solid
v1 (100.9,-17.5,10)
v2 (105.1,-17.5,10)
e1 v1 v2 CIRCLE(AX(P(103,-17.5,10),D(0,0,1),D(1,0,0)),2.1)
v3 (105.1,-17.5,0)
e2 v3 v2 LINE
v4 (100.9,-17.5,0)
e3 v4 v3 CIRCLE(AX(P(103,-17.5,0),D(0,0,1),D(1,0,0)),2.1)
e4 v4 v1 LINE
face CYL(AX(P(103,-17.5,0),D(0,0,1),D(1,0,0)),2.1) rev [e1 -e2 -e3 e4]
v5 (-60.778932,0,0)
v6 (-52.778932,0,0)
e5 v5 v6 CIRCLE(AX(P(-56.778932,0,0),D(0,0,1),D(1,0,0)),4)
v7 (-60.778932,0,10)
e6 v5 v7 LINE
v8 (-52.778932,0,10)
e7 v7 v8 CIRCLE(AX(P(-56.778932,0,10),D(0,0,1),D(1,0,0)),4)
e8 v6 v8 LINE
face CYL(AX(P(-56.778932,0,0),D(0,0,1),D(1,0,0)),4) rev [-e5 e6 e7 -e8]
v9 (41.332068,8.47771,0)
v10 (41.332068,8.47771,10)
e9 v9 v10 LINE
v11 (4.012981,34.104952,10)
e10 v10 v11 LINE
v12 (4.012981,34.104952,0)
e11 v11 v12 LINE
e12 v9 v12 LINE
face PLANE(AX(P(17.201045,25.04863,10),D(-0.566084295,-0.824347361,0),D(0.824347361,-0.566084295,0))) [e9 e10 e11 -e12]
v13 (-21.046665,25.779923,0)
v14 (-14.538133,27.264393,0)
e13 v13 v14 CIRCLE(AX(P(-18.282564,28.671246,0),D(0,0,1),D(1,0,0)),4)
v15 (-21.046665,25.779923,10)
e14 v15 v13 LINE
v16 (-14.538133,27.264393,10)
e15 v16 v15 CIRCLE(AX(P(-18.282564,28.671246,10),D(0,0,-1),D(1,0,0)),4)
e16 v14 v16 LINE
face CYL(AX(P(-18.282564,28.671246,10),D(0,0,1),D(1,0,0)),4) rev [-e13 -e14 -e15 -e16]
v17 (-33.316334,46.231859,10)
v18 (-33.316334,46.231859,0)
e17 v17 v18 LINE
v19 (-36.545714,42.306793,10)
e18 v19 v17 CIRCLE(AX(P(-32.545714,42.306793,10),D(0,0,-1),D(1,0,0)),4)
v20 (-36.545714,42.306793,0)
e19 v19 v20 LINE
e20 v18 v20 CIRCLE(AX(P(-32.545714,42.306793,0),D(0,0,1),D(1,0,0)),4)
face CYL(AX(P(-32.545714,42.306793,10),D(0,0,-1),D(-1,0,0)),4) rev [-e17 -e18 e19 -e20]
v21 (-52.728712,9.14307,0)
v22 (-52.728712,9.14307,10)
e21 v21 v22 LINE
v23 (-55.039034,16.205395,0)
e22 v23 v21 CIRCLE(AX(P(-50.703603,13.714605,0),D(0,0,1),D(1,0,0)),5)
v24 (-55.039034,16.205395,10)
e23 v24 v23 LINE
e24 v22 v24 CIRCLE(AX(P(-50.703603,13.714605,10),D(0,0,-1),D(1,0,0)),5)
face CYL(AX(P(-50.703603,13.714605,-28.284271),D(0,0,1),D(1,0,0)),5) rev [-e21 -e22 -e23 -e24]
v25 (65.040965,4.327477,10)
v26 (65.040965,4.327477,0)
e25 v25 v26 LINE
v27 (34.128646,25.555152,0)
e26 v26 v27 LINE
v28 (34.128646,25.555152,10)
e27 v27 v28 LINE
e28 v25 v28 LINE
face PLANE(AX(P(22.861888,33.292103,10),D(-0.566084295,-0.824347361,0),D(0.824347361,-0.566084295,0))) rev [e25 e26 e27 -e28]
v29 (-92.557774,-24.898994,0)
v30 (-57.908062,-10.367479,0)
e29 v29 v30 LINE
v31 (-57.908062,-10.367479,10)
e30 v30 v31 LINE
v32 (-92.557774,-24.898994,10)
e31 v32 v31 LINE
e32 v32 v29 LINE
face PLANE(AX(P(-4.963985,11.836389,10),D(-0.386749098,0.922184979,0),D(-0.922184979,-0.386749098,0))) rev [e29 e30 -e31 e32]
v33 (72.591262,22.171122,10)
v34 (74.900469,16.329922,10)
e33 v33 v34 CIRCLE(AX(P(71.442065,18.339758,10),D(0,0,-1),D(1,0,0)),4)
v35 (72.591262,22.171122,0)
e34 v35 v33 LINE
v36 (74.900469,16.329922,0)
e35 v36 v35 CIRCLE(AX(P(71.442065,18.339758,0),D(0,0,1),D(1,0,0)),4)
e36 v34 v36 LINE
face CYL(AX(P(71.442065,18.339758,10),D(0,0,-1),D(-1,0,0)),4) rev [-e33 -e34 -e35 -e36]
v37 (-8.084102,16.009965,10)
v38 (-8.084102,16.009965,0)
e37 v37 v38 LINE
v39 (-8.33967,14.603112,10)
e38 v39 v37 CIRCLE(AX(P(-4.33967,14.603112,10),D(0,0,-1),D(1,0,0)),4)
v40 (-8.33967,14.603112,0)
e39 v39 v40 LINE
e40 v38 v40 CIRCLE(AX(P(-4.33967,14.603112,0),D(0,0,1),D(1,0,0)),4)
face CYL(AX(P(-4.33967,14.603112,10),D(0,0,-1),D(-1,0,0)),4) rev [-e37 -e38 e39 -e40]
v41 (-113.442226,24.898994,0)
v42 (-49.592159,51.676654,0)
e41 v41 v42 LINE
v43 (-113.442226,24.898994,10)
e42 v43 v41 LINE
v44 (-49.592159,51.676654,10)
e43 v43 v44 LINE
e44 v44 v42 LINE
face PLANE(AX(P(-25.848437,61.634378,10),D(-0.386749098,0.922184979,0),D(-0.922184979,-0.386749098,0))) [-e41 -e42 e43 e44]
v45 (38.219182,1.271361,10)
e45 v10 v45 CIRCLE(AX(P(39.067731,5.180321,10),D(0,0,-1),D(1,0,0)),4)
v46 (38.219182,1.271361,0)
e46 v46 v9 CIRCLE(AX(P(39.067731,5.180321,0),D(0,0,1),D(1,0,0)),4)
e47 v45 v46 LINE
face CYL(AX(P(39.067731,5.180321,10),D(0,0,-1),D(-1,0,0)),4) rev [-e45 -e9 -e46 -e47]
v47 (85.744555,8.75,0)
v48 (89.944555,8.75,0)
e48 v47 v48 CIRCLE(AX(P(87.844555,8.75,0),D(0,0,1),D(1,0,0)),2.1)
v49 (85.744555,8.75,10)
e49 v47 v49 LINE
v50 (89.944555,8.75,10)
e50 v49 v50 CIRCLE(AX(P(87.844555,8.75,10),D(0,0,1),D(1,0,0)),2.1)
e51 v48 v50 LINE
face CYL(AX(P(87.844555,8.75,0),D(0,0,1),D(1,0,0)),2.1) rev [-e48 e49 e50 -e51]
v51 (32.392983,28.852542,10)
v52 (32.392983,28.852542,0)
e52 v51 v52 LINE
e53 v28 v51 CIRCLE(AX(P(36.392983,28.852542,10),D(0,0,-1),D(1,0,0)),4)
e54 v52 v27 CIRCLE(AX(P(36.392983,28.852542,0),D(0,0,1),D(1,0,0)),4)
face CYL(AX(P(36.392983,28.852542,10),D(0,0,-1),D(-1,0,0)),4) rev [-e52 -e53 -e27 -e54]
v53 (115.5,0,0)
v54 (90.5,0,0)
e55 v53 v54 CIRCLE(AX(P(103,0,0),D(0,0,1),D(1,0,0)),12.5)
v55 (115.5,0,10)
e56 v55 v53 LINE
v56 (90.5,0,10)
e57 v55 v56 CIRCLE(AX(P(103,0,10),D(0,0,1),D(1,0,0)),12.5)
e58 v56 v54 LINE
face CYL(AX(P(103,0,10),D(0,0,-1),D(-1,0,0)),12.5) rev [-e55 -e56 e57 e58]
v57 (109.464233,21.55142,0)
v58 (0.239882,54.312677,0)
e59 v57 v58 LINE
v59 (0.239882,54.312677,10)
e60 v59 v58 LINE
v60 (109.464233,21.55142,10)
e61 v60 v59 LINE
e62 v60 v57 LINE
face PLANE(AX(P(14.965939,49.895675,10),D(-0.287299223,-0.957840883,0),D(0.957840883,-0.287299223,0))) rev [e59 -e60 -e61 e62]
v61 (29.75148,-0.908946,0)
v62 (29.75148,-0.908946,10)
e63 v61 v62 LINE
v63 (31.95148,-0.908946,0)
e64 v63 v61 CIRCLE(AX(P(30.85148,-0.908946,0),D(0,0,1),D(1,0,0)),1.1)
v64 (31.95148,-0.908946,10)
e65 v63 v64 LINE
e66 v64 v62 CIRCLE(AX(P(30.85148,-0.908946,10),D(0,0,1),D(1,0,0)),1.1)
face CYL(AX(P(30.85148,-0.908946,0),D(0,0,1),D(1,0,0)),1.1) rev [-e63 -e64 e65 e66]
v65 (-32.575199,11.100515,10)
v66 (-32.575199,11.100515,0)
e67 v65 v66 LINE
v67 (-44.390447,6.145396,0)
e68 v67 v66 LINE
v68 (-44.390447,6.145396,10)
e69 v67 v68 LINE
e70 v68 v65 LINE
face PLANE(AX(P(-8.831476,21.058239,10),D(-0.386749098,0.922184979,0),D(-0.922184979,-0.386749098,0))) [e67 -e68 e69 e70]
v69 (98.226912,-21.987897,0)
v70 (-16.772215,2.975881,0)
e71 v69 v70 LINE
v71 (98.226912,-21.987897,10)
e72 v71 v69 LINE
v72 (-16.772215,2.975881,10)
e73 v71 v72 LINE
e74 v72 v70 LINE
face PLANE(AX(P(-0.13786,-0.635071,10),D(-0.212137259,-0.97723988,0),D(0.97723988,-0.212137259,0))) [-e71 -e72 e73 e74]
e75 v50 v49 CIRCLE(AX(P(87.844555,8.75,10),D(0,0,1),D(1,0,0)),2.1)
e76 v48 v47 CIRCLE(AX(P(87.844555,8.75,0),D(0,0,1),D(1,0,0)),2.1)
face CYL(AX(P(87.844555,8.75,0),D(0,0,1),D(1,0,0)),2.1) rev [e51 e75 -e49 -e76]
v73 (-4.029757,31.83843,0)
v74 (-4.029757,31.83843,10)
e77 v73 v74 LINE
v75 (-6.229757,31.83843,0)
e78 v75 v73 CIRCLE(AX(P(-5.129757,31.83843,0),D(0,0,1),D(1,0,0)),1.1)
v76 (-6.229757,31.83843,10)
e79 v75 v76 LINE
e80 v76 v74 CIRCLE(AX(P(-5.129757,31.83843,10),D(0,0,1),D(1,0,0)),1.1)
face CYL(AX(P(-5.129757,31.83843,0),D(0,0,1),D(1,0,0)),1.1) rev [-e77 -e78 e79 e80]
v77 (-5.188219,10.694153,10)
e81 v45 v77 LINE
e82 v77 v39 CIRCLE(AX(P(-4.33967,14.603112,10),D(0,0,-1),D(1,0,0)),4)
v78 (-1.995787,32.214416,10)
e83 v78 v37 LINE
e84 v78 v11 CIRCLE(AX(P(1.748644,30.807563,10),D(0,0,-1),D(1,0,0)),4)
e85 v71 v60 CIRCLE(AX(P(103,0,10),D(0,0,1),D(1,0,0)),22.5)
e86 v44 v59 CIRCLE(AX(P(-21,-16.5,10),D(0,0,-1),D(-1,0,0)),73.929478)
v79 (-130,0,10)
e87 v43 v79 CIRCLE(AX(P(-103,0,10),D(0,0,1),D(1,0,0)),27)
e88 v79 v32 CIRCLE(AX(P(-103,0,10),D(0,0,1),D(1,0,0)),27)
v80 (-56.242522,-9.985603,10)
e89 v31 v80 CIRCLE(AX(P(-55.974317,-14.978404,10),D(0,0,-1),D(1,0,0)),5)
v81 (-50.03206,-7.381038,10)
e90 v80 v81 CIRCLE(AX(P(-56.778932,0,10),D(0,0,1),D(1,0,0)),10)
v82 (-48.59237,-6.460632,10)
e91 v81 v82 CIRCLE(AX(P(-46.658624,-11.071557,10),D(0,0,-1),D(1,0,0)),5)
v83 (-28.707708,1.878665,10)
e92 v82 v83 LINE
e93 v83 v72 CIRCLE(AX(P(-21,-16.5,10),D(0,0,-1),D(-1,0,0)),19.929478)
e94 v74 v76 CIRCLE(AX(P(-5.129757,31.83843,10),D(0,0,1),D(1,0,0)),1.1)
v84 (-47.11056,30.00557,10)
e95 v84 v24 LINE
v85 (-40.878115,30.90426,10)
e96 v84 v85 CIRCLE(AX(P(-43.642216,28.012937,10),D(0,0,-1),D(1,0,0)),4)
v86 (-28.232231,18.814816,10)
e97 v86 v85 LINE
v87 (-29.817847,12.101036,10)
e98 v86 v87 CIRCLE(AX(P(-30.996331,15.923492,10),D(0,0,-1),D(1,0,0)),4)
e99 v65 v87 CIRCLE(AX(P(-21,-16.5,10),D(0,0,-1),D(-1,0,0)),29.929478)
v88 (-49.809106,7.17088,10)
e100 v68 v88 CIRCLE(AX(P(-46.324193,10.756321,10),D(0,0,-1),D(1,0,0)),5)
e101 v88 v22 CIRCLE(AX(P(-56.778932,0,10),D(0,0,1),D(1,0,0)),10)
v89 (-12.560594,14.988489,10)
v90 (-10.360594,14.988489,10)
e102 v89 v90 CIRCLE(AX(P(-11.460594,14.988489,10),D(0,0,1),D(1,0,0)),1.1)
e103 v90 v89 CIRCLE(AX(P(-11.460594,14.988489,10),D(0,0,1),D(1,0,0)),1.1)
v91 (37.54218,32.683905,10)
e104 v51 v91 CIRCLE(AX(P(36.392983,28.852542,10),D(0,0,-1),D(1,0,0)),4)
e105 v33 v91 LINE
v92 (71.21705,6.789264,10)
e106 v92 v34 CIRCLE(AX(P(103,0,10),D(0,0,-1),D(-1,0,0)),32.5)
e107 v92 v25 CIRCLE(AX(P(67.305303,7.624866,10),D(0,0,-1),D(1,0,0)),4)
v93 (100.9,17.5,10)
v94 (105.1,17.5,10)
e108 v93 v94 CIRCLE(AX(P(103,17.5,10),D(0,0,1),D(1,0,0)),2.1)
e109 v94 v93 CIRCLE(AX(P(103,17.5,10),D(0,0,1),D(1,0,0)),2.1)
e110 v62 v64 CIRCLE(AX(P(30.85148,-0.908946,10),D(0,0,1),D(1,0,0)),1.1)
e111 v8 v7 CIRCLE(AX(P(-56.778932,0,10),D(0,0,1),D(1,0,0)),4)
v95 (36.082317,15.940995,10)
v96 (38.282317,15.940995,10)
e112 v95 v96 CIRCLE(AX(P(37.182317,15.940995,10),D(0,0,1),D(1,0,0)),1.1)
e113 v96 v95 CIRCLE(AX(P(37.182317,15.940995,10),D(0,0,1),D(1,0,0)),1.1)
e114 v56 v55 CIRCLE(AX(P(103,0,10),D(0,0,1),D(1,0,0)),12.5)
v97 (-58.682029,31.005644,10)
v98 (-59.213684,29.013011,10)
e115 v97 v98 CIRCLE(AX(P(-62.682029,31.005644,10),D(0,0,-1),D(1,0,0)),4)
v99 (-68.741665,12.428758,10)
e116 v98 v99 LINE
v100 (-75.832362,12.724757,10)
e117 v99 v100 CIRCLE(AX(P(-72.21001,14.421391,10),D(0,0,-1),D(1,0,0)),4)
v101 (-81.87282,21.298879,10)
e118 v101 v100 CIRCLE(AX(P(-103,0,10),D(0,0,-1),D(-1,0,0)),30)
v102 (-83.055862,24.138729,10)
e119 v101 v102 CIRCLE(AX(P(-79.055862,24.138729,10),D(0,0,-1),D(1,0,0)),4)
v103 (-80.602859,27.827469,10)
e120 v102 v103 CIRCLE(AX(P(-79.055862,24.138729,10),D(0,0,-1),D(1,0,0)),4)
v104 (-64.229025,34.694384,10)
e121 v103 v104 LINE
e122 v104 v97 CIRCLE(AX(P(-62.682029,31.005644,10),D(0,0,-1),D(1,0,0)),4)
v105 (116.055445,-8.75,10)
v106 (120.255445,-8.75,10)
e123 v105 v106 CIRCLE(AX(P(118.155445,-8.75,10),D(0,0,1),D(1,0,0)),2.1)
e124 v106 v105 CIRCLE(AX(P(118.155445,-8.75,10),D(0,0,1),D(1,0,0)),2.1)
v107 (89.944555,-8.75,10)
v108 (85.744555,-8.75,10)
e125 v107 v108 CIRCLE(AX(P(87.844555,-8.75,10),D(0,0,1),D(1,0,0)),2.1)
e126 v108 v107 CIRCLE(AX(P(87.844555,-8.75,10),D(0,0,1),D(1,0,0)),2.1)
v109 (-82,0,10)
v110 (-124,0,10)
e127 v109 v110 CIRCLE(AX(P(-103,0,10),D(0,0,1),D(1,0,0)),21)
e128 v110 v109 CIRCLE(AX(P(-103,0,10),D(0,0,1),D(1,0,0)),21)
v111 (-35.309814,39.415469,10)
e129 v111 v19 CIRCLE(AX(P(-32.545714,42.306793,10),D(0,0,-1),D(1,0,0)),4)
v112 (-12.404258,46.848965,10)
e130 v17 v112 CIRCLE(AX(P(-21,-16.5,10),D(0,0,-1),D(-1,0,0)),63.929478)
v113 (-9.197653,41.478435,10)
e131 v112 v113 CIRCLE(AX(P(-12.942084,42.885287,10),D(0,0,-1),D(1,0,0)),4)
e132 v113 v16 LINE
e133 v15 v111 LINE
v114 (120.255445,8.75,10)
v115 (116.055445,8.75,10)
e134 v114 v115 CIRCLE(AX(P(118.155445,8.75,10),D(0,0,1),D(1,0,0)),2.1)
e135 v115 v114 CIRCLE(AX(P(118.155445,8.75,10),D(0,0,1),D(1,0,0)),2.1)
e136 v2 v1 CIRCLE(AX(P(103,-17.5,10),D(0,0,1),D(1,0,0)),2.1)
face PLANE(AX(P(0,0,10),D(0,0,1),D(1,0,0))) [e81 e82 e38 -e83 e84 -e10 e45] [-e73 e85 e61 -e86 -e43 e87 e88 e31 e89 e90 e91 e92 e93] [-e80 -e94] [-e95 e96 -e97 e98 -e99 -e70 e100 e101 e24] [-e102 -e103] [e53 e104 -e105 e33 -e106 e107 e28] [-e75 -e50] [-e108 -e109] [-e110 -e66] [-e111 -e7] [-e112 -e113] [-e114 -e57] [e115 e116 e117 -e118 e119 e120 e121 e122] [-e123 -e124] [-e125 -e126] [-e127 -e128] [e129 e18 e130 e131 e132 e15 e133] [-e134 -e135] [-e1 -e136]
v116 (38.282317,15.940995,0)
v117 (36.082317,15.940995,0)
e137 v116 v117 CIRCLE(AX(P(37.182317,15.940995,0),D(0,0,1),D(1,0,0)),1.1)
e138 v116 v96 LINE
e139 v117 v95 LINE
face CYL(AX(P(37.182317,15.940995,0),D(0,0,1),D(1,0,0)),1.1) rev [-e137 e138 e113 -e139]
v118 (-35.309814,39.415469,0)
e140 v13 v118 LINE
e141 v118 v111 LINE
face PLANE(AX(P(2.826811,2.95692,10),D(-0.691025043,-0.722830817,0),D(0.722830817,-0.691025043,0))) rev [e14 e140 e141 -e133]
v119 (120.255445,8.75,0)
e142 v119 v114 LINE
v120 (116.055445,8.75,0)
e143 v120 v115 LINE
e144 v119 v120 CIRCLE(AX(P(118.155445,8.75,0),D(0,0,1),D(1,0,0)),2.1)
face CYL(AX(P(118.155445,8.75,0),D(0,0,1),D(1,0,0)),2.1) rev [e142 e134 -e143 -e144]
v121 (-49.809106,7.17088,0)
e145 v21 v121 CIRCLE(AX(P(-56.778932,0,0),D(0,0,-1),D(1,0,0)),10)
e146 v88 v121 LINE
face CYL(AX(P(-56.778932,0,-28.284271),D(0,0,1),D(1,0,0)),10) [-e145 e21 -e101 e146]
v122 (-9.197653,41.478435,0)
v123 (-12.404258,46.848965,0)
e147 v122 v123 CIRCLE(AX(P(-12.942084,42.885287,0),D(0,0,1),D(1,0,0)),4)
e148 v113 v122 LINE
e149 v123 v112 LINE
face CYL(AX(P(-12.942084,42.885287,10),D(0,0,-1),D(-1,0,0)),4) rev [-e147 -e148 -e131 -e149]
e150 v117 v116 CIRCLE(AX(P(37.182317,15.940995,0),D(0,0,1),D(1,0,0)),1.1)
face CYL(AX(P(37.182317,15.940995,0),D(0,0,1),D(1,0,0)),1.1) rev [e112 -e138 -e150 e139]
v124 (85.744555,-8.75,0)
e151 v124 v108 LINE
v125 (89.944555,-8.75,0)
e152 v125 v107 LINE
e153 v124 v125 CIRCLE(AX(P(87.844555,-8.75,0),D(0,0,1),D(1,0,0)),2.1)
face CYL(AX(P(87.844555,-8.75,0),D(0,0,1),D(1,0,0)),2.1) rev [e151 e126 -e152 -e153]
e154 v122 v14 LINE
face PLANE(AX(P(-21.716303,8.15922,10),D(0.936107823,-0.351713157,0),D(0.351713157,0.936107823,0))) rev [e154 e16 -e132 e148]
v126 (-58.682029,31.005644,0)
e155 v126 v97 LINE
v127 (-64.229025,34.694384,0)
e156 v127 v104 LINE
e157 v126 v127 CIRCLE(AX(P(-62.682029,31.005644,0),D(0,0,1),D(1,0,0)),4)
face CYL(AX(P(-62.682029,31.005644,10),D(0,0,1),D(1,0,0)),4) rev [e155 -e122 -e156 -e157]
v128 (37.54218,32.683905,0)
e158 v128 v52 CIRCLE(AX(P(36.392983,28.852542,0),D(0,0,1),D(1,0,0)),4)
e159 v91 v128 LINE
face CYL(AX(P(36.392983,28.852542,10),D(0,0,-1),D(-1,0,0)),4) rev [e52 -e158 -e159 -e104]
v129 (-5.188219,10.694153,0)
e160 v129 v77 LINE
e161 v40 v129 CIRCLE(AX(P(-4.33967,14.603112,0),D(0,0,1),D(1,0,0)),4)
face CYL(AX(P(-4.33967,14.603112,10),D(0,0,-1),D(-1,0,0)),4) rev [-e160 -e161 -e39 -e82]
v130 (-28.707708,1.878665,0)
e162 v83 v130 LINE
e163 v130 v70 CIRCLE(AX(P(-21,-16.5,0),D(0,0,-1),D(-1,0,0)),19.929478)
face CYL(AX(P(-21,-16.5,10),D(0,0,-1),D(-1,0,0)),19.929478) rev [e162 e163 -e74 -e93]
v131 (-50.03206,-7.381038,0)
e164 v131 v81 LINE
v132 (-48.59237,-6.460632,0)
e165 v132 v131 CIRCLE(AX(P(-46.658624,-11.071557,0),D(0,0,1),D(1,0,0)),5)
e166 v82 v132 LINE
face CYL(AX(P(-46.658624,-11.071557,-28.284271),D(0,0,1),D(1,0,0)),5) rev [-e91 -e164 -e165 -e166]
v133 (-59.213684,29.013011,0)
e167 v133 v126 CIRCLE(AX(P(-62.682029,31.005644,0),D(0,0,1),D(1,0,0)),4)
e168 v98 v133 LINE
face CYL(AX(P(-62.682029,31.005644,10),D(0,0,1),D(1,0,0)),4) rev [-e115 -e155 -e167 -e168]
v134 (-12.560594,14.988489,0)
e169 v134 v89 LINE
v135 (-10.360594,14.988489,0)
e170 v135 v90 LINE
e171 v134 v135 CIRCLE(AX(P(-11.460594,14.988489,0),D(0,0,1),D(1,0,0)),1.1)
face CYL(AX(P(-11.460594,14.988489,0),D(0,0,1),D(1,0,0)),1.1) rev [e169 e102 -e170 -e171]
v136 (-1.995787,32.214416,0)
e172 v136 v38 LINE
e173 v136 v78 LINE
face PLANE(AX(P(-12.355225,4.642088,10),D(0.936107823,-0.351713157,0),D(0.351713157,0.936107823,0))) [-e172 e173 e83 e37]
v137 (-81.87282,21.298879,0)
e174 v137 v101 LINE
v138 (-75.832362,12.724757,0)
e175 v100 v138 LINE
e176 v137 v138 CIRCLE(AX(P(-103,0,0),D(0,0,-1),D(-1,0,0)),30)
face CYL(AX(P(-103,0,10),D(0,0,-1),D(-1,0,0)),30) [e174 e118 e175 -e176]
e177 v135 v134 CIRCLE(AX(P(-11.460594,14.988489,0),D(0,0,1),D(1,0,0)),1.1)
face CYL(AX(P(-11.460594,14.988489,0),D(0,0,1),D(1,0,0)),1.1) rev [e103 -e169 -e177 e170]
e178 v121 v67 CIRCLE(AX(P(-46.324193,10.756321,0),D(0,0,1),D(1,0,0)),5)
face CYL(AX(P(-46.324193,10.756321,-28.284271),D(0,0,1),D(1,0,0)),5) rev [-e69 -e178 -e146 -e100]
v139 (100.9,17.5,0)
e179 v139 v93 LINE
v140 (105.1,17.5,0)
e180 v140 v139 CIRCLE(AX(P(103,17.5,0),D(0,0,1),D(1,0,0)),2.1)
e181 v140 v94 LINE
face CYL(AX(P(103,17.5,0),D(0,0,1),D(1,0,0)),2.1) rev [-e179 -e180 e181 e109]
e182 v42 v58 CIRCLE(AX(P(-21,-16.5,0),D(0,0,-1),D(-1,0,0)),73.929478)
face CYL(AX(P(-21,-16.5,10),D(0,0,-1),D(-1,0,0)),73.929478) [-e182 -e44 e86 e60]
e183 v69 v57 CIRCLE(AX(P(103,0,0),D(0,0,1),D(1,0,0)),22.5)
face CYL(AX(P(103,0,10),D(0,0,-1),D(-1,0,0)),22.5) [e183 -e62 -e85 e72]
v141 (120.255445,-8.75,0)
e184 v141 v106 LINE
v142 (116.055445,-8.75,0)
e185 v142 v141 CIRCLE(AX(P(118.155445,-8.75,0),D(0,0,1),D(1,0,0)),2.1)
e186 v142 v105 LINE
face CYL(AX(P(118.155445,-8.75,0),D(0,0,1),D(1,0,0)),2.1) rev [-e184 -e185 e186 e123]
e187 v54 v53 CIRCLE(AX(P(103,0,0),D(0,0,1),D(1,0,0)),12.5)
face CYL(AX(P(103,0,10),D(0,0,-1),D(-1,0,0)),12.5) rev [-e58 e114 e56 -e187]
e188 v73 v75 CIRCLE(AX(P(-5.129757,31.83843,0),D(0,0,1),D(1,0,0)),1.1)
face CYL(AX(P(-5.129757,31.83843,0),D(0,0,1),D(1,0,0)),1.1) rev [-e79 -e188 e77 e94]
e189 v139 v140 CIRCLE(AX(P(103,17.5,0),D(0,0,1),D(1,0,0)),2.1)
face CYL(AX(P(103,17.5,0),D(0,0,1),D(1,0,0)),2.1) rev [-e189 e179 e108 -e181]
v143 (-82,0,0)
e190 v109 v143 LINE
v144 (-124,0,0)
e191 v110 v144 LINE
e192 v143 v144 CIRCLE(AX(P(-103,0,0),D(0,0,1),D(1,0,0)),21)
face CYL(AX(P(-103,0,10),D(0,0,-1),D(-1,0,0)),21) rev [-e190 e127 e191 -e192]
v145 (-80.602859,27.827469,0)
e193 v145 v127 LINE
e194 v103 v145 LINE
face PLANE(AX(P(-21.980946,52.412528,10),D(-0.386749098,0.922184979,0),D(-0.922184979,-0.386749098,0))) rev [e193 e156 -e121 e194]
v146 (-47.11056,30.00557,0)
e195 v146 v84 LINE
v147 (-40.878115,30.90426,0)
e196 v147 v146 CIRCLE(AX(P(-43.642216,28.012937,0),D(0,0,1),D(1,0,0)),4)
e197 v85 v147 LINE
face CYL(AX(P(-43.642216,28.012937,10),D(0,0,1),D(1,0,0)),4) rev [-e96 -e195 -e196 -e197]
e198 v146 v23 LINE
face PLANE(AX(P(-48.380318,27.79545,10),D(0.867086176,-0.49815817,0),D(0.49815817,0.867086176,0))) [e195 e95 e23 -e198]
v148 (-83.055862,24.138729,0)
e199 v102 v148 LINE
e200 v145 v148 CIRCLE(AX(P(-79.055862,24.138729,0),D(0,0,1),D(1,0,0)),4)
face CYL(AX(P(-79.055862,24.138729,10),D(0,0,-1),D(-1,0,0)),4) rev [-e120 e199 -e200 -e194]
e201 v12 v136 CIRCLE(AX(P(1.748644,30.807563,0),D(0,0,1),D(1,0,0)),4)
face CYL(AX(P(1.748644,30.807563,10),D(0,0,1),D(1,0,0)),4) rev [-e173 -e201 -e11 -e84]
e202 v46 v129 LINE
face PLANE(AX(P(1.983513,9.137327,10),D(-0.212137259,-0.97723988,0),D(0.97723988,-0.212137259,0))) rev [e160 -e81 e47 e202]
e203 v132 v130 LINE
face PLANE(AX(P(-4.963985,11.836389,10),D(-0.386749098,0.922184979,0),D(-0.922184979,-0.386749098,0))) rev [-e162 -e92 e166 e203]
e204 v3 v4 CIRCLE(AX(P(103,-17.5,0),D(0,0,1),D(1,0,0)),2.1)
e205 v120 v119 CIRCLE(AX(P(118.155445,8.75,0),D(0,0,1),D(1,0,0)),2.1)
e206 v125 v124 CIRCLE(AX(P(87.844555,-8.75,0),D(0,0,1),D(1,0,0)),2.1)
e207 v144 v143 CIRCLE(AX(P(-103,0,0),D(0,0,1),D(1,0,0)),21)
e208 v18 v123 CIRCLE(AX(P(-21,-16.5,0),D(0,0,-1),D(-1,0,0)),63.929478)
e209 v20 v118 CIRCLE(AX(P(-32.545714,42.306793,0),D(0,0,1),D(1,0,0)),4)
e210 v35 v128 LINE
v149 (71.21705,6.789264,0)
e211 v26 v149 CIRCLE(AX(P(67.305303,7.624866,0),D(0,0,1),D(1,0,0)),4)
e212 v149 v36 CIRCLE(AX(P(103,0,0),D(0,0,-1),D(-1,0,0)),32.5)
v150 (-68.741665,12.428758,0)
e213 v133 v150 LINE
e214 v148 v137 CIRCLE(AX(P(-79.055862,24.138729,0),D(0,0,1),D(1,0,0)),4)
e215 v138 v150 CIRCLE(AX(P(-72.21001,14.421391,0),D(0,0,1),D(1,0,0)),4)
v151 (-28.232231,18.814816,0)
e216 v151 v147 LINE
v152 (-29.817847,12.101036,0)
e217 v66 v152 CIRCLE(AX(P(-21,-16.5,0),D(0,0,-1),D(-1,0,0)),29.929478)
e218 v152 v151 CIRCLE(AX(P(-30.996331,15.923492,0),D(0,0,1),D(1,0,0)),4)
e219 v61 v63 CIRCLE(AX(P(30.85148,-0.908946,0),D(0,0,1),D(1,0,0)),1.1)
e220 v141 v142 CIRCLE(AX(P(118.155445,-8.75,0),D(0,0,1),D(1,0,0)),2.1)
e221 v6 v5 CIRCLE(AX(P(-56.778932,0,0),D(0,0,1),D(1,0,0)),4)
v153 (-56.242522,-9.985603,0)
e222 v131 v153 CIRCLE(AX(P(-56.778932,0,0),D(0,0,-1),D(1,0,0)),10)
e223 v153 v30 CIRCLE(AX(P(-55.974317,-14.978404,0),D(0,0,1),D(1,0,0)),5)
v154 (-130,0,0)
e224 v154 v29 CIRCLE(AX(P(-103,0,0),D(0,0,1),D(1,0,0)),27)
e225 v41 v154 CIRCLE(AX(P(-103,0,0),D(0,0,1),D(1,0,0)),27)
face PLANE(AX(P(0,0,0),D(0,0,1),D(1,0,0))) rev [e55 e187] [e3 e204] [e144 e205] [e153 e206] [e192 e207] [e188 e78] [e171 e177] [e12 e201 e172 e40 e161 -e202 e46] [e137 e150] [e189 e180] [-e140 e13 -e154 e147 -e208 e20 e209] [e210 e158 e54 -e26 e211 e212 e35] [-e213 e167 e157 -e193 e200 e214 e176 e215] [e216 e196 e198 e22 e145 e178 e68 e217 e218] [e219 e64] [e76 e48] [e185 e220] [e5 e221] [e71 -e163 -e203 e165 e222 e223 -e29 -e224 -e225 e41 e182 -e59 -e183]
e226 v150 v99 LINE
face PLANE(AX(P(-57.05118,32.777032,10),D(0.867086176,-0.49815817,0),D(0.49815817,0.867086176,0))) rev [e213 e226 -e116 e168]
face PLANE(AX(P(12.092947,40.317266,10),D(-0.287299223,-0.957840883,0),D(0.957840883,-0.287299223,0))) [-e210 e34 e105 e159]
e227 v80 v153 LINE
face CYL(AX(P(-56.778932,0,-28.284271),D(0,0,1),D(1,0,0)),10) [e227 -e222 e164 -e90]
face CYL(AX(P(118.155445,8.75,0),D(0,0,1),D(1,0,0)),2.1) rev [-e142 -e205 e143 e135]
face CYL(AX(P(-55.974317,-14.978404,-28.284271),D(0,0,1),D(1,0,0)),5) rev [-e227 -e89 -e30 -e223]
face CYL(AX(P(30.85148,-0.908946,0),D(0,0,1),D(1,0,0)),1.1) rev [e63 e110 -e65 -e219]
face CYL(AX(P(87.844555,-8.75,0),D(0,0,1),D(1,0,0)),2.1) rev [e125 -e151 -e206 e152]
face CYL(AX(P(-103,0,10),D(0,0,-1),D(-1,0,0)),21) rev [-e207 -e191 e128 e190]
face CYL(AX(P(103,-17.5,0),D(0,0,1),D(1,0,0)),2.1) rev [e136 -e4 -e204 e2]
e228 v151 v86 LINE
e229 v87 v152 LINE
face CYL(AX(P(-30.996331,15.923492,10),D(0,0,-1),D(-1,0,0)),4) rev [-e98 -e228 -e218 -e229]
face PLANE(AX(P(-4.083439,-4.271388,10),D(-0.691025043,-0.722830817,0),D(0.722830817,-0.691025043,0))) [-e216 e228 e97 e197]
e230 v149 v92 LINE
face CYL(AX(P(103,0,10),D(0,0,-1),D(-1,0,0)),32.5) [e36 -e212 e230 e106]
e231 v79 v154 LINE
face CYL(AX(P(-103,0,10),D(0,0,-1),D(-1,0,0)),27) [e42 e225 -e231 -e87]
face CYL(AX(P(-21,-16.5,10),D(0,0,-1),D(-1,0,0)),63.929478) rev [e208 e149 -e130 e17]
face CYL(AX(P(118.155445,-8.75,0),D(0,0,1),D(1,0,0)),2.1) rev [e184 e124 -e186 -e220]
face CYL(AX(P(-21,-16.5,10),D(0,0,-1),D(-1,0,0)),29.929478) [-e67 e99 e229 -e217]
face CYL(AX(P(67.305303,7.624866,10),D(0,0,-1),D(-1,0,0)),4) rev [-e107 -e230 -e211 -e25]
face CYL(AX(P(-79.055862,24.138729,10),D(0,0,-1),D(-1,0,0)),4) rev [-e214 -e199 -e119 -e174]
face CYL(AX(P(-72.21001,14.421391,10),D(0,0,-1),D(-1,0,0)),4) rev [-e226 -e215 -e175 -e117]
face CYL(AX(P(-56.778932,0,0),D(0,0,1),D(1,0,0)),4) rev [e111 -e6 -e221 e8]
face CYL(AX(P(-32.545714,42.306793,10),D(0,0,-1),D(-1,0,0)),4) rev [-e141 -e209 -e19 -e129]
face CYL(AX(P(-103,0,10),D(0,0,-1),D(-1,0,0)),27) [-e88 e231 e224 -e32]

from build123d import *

# Parameters (mm, degrees)
SKETCH_1_R          = 21
SKETCH_1_R_2        = 12.5
EXTRUDE_1_DEPTH     = 10
EXTRUDE_3_DEPTH     = 10
CUT_EXTRUDE_1_DEPTH = 143.471558445
CUT_EXTRUDE_2_DEPTH = 143.471558445
FILLET_1_R          = 4
SKETCH_4_R          = 2.1
CUT_EXTRUDE_3_DEPTH = 143.471558445
SKETCH_5_R          = 4
CUT_EXTRUDE_4_DEPTH = 10
SKETCH_6_R          = 10
SKETCH_6_R_2        = 4
EXTRUDE_4_DEPTH     = 10
FILLET_2_R          = 5
SKETCH_7_R          = 1.1
CUT_EXTRUDE_5_DEPTH = 10


with BuildPart() as part:
    # 草图1 → 凸台-拉伸1 (new body)
    with BuildSketch(Plane.XY):
        with BuildLine():
            ThreePointArc((-102.410194175, 26.993557177), (-130, 0), (-102.410194175, -26.993557177))
            Line((-102.410194175, -26.993557177), (103.491504854, -22.494630981))
            ThreePointArc((103.491504854, -22.494630981), (125.5, 0), (103.491504854, 22.494630981))
            Line((103.491504854, 22.494630981), (-102.410194175, 26.993557177))
        make_face()
        with Locations((-103, 0)):
            Circle(SKETCH_1_R, mode=Mode.SUBTRACT)
        with Locations((103, 0)):
            Circle(SKETCH_1_R_2, mode=Mode.SUBTRACT)
    extrude(amount=EXTRUDE_1_DEPTH)

    # 草图2 → 凸台-拉伸3 (add)
    with BuildSketch(Plane(origin=(0, 0, 0), x_dir=(-1, 0, 0), z_dir=(0, 0, -1))):
        with BuildLine():
            Line((-103.491504854, 22.494630981), (-40.939702548, 23.861379985))
            ThreePointArc((-40.939702548, 23.861379985), (-23.289176704, 42.694903268), (-0.239881629, 54.312676651))
            Line((-0.239881629, 54.312676651), (-109.464232513, 21.551419861))
            ThreePointArc((-109.464232513, 21.551419861), (-106.509698333, 22.224581382), (-103.491504854, 22.494630981))
        make_face()
        with BuildLine():
            ThreePointArc((-0.239881629, 54.312676651), (-23.289176704, 42.694903268), (-40.939702548, 23.861379985))
            Line((-40.939702548, 23.861379985), (81.117648154, 26.528317728))
            ThreePointArc((81.117648154, 26.528317728), (67.102789284, 41.29360316), (49.592159014, 51.676654281))
            ThreePointArc((49.592159014, 51.676654281), (24.905271972, 57.326259535), (-0.239881629, 54.312676651))
        make_face()
        with BuildLine():
            ThreePointArc((49.592159014, 51.676654281), (67.102789284, 41.29360316), (81.117648154, 26.528317728))
            Line((81.117648154, 26.528317728), (102.410194175, 26.993557177))
            ThreePointArc((102.410194175, 26.993557177), (108.03630245, 26.526131599), (113.442225649, 24.898994428))
            Line((113.442225649, 24.898994428), (49.592159014, 51.676654281))
        make_face()
    extrude(amount=-EXTRUDE_3_DEPTH)

    # 草图2<4> → 切除-拉伸1 (cut, through all)
    with BuildSketch(Plane(origin=(0, 0, 0), x_dir=(-1, 0, 0), z_dir=(0, 0, -1))):
        with BuildLine():
            ThreePointArc((-98.226911662, -21.987897301), (-100.844267169, -22.396491153), (-103.491504854, -22.494630981))
            Line((-103.491504854, -22.494630981), (102.410194175, -26.993557177))
            ThreePointArc((102.410194175, -26.993557177), (97.385444996, -26.409785537), (92.557774351, -24.898994428))
            Line((92.557774351, -24.898994428), (28.707707717, 1.878665426))
            ThreePointArc((28.707707717, 1.878665426), (22.824400221, 3.34579716), (16.772215113, 2.97588088))
            Line((16.772215113, 2.97588088), (-98.226911662, -21.987897301))
        make_face()
    extrude(amount=-CUT_EXTRUDE_1_DEPTH, mode=Mode.SUBTRACT)

    # 草图3 → 切除-拉伸2 (cut, through all)
    with BuildSketch(Plane(origin=(0, 0, 0), x_dir=(-1, 0, 0), z_dir=(0, 0, -1))):
        with BuildLine():
            Line((-13.049437663, 40.030371792), (-77.856013804, 20.591987718))
            ThreePointArc((-77.856013804, 20.591987718), (-72.492161336, 11.2036503), (-70.505090985, 0.57522877))
            Line((-70.505090985, 0.57522877), (-13.049437663, 40.030371792))
        make_face()
        Polygon((0.198802543, 36.997209558), (-58.115751128, -3.047745505), (9.712361202, 11.67624413), align=None)
        with BuildLine():
            ThreePointArc((40.504408652, 44.381493291), (24.109384021, 47.353816747), (7.503136565, 45.988501819))
            Line((7.503136565, 45.988501819), (16.668465779, 21.594372082))
            Line((16.668465779, 21.594372082), (40.504408652, 44.381493291))
        make_face()
        with BuildLine():
            Line((44.567749988, 34.431544826), (22.556649299, 13.38896967))
            ThreePointArc((22.556649299, 13.38896967), (27.664879137, 12.677954881), (32.575198698, 11.100515214))
            Line((32.575198698, 11.100515214), (66.033457739, -2.931324174))
            Line((66.033457739, -2.931324174), (44.567749988, 34.431544826))
        make_face()
        with BuildLine():
            Line((86.779784403, 25.236969033), (53.321525362, 39.268808421))
            Line((53.321525362, 39.268808421), (73.33058295, 4.441361493))
            ThreePointArc((73.33058295, 4.441361493), (77.809150087, 16.291748852), (86.779784403, 25.236969033))
        make_face()
    extrude(amount=-CUT_EXTRUDE_2_DEPTH, mode=Mode.SUBTRACT)

    # 圆角1
    fillet_1_edges = [part.edges().sort_by_distance(p)[0] for p in [
        (-86.779784403, 25.236969033, 5),
        (-73.33058295, 4.441361493, 5),
        (-53.321525362, 39.268808421, 5),
        (-22.556649299, 13.38896967, 5),
        (-44.567749988, 34.431544826, 5),
        (-66.033457739, -2.931324174, 5),
        (70.505090985, 0.57522877, 5),
        (77.856013804, 20.591987718, 5),
        (13.049437663, 40.030371792, 5),
        (-40.504408652, 44.381493291, 5),
        (-16.668465779, 21.594372082, 5),
        (-7.503136565, 45.988501819, 5),
        (-0.198802543, 36.997209558, 5),
        (-9.712361202, 11.67624413, 5),
        (58.115751128, -3.047745505, 5),
    ]]
    fillet(fillet_1_edges, radius=FILLET_1_R)

    # 草图4 → 切除-拉伸3 (cut, through all)
    with BuildSketch(Plane.XY.offset(10)):
        with Locations((103, 17.5)):
            Circle(SKETCH_4_R)
        with Locations((118.155444566, 8.75)):
            Circle(SKETCH_4_R)
        with Locations((118.155444566, -8.75)):
            Circle(SKETCH_4_R)
        with Locations((103, -17.5)):
            Circle(SKETCH_4_R)
        with Locations((87.844555434, -8.75)):
            Circle(SKETCH_4_R)
        with Locations((87.844555434, 8.75)):
            Circle(SKETCH_4_R)
    extrude(amount=-CUT_EXTRUDE_3_DEPTH, mode=Mode.SUBTRACT)

    # 草图5 → 切除-拉伸4 (cut)
    with BuildSketch(Plane.XY.offset(10)):
        with Locations((-56.77893166, 0)):
            Circle(SKETCH_5_R)
    extrude(amount=-CUT_EXTRUDE_4_DEPTH, mode=Mode.SUBTRACT)

    # 草图6 → 凸台-拉伸4 (add)
    with BuildSketch(Plane.XY.offset(10)):
        with Locations((-56.77893166, 0)):
            Circle(SKETCH_6_R)
        with Locations((-56.77893166, 0)):
            Circle(SKETCH_6_R_2, mode=Mode.SUBTRACT)
    extrude(amount=-EXTRUDE_4_DEPTH)

    # 圆角2
    fillet_2_edges = [part.edges().sort_by_distance(p)[0] for p in [
        (-47.931305001, 4.660418705, 5),
        (-57.024626927, -9.996981236, 5),
        (-49.475805199, -6.831130499, 5),
        (-58.71258633, 9.811267992, 5),
    ]]
    fillet(fillet_2_edges, radius=FILLET_2_R)

    # 草图7 → 切除-拉伸5 (cut)
    with BuildSketch(Plane.XY.offset(10)):
        with Locations((-5.129756774, 31.838429538)):
            Circle(SKETCH_7_R)
        with Locations((-11.460593594, 14.988488732)):
            Circle(SKETCH_7_R)
        with Locations((37.182316805, 15.940994857)):
            Circle(SKETCH_7_R)
        with Locations((30.851479985, -0.908945949)):
            Circle(SKETCH_7_R)
    extrude(amount=-CUT_EXTRUDE_5_DEPTH, mode=Mode.SUBTRACT)


solid = part.part
